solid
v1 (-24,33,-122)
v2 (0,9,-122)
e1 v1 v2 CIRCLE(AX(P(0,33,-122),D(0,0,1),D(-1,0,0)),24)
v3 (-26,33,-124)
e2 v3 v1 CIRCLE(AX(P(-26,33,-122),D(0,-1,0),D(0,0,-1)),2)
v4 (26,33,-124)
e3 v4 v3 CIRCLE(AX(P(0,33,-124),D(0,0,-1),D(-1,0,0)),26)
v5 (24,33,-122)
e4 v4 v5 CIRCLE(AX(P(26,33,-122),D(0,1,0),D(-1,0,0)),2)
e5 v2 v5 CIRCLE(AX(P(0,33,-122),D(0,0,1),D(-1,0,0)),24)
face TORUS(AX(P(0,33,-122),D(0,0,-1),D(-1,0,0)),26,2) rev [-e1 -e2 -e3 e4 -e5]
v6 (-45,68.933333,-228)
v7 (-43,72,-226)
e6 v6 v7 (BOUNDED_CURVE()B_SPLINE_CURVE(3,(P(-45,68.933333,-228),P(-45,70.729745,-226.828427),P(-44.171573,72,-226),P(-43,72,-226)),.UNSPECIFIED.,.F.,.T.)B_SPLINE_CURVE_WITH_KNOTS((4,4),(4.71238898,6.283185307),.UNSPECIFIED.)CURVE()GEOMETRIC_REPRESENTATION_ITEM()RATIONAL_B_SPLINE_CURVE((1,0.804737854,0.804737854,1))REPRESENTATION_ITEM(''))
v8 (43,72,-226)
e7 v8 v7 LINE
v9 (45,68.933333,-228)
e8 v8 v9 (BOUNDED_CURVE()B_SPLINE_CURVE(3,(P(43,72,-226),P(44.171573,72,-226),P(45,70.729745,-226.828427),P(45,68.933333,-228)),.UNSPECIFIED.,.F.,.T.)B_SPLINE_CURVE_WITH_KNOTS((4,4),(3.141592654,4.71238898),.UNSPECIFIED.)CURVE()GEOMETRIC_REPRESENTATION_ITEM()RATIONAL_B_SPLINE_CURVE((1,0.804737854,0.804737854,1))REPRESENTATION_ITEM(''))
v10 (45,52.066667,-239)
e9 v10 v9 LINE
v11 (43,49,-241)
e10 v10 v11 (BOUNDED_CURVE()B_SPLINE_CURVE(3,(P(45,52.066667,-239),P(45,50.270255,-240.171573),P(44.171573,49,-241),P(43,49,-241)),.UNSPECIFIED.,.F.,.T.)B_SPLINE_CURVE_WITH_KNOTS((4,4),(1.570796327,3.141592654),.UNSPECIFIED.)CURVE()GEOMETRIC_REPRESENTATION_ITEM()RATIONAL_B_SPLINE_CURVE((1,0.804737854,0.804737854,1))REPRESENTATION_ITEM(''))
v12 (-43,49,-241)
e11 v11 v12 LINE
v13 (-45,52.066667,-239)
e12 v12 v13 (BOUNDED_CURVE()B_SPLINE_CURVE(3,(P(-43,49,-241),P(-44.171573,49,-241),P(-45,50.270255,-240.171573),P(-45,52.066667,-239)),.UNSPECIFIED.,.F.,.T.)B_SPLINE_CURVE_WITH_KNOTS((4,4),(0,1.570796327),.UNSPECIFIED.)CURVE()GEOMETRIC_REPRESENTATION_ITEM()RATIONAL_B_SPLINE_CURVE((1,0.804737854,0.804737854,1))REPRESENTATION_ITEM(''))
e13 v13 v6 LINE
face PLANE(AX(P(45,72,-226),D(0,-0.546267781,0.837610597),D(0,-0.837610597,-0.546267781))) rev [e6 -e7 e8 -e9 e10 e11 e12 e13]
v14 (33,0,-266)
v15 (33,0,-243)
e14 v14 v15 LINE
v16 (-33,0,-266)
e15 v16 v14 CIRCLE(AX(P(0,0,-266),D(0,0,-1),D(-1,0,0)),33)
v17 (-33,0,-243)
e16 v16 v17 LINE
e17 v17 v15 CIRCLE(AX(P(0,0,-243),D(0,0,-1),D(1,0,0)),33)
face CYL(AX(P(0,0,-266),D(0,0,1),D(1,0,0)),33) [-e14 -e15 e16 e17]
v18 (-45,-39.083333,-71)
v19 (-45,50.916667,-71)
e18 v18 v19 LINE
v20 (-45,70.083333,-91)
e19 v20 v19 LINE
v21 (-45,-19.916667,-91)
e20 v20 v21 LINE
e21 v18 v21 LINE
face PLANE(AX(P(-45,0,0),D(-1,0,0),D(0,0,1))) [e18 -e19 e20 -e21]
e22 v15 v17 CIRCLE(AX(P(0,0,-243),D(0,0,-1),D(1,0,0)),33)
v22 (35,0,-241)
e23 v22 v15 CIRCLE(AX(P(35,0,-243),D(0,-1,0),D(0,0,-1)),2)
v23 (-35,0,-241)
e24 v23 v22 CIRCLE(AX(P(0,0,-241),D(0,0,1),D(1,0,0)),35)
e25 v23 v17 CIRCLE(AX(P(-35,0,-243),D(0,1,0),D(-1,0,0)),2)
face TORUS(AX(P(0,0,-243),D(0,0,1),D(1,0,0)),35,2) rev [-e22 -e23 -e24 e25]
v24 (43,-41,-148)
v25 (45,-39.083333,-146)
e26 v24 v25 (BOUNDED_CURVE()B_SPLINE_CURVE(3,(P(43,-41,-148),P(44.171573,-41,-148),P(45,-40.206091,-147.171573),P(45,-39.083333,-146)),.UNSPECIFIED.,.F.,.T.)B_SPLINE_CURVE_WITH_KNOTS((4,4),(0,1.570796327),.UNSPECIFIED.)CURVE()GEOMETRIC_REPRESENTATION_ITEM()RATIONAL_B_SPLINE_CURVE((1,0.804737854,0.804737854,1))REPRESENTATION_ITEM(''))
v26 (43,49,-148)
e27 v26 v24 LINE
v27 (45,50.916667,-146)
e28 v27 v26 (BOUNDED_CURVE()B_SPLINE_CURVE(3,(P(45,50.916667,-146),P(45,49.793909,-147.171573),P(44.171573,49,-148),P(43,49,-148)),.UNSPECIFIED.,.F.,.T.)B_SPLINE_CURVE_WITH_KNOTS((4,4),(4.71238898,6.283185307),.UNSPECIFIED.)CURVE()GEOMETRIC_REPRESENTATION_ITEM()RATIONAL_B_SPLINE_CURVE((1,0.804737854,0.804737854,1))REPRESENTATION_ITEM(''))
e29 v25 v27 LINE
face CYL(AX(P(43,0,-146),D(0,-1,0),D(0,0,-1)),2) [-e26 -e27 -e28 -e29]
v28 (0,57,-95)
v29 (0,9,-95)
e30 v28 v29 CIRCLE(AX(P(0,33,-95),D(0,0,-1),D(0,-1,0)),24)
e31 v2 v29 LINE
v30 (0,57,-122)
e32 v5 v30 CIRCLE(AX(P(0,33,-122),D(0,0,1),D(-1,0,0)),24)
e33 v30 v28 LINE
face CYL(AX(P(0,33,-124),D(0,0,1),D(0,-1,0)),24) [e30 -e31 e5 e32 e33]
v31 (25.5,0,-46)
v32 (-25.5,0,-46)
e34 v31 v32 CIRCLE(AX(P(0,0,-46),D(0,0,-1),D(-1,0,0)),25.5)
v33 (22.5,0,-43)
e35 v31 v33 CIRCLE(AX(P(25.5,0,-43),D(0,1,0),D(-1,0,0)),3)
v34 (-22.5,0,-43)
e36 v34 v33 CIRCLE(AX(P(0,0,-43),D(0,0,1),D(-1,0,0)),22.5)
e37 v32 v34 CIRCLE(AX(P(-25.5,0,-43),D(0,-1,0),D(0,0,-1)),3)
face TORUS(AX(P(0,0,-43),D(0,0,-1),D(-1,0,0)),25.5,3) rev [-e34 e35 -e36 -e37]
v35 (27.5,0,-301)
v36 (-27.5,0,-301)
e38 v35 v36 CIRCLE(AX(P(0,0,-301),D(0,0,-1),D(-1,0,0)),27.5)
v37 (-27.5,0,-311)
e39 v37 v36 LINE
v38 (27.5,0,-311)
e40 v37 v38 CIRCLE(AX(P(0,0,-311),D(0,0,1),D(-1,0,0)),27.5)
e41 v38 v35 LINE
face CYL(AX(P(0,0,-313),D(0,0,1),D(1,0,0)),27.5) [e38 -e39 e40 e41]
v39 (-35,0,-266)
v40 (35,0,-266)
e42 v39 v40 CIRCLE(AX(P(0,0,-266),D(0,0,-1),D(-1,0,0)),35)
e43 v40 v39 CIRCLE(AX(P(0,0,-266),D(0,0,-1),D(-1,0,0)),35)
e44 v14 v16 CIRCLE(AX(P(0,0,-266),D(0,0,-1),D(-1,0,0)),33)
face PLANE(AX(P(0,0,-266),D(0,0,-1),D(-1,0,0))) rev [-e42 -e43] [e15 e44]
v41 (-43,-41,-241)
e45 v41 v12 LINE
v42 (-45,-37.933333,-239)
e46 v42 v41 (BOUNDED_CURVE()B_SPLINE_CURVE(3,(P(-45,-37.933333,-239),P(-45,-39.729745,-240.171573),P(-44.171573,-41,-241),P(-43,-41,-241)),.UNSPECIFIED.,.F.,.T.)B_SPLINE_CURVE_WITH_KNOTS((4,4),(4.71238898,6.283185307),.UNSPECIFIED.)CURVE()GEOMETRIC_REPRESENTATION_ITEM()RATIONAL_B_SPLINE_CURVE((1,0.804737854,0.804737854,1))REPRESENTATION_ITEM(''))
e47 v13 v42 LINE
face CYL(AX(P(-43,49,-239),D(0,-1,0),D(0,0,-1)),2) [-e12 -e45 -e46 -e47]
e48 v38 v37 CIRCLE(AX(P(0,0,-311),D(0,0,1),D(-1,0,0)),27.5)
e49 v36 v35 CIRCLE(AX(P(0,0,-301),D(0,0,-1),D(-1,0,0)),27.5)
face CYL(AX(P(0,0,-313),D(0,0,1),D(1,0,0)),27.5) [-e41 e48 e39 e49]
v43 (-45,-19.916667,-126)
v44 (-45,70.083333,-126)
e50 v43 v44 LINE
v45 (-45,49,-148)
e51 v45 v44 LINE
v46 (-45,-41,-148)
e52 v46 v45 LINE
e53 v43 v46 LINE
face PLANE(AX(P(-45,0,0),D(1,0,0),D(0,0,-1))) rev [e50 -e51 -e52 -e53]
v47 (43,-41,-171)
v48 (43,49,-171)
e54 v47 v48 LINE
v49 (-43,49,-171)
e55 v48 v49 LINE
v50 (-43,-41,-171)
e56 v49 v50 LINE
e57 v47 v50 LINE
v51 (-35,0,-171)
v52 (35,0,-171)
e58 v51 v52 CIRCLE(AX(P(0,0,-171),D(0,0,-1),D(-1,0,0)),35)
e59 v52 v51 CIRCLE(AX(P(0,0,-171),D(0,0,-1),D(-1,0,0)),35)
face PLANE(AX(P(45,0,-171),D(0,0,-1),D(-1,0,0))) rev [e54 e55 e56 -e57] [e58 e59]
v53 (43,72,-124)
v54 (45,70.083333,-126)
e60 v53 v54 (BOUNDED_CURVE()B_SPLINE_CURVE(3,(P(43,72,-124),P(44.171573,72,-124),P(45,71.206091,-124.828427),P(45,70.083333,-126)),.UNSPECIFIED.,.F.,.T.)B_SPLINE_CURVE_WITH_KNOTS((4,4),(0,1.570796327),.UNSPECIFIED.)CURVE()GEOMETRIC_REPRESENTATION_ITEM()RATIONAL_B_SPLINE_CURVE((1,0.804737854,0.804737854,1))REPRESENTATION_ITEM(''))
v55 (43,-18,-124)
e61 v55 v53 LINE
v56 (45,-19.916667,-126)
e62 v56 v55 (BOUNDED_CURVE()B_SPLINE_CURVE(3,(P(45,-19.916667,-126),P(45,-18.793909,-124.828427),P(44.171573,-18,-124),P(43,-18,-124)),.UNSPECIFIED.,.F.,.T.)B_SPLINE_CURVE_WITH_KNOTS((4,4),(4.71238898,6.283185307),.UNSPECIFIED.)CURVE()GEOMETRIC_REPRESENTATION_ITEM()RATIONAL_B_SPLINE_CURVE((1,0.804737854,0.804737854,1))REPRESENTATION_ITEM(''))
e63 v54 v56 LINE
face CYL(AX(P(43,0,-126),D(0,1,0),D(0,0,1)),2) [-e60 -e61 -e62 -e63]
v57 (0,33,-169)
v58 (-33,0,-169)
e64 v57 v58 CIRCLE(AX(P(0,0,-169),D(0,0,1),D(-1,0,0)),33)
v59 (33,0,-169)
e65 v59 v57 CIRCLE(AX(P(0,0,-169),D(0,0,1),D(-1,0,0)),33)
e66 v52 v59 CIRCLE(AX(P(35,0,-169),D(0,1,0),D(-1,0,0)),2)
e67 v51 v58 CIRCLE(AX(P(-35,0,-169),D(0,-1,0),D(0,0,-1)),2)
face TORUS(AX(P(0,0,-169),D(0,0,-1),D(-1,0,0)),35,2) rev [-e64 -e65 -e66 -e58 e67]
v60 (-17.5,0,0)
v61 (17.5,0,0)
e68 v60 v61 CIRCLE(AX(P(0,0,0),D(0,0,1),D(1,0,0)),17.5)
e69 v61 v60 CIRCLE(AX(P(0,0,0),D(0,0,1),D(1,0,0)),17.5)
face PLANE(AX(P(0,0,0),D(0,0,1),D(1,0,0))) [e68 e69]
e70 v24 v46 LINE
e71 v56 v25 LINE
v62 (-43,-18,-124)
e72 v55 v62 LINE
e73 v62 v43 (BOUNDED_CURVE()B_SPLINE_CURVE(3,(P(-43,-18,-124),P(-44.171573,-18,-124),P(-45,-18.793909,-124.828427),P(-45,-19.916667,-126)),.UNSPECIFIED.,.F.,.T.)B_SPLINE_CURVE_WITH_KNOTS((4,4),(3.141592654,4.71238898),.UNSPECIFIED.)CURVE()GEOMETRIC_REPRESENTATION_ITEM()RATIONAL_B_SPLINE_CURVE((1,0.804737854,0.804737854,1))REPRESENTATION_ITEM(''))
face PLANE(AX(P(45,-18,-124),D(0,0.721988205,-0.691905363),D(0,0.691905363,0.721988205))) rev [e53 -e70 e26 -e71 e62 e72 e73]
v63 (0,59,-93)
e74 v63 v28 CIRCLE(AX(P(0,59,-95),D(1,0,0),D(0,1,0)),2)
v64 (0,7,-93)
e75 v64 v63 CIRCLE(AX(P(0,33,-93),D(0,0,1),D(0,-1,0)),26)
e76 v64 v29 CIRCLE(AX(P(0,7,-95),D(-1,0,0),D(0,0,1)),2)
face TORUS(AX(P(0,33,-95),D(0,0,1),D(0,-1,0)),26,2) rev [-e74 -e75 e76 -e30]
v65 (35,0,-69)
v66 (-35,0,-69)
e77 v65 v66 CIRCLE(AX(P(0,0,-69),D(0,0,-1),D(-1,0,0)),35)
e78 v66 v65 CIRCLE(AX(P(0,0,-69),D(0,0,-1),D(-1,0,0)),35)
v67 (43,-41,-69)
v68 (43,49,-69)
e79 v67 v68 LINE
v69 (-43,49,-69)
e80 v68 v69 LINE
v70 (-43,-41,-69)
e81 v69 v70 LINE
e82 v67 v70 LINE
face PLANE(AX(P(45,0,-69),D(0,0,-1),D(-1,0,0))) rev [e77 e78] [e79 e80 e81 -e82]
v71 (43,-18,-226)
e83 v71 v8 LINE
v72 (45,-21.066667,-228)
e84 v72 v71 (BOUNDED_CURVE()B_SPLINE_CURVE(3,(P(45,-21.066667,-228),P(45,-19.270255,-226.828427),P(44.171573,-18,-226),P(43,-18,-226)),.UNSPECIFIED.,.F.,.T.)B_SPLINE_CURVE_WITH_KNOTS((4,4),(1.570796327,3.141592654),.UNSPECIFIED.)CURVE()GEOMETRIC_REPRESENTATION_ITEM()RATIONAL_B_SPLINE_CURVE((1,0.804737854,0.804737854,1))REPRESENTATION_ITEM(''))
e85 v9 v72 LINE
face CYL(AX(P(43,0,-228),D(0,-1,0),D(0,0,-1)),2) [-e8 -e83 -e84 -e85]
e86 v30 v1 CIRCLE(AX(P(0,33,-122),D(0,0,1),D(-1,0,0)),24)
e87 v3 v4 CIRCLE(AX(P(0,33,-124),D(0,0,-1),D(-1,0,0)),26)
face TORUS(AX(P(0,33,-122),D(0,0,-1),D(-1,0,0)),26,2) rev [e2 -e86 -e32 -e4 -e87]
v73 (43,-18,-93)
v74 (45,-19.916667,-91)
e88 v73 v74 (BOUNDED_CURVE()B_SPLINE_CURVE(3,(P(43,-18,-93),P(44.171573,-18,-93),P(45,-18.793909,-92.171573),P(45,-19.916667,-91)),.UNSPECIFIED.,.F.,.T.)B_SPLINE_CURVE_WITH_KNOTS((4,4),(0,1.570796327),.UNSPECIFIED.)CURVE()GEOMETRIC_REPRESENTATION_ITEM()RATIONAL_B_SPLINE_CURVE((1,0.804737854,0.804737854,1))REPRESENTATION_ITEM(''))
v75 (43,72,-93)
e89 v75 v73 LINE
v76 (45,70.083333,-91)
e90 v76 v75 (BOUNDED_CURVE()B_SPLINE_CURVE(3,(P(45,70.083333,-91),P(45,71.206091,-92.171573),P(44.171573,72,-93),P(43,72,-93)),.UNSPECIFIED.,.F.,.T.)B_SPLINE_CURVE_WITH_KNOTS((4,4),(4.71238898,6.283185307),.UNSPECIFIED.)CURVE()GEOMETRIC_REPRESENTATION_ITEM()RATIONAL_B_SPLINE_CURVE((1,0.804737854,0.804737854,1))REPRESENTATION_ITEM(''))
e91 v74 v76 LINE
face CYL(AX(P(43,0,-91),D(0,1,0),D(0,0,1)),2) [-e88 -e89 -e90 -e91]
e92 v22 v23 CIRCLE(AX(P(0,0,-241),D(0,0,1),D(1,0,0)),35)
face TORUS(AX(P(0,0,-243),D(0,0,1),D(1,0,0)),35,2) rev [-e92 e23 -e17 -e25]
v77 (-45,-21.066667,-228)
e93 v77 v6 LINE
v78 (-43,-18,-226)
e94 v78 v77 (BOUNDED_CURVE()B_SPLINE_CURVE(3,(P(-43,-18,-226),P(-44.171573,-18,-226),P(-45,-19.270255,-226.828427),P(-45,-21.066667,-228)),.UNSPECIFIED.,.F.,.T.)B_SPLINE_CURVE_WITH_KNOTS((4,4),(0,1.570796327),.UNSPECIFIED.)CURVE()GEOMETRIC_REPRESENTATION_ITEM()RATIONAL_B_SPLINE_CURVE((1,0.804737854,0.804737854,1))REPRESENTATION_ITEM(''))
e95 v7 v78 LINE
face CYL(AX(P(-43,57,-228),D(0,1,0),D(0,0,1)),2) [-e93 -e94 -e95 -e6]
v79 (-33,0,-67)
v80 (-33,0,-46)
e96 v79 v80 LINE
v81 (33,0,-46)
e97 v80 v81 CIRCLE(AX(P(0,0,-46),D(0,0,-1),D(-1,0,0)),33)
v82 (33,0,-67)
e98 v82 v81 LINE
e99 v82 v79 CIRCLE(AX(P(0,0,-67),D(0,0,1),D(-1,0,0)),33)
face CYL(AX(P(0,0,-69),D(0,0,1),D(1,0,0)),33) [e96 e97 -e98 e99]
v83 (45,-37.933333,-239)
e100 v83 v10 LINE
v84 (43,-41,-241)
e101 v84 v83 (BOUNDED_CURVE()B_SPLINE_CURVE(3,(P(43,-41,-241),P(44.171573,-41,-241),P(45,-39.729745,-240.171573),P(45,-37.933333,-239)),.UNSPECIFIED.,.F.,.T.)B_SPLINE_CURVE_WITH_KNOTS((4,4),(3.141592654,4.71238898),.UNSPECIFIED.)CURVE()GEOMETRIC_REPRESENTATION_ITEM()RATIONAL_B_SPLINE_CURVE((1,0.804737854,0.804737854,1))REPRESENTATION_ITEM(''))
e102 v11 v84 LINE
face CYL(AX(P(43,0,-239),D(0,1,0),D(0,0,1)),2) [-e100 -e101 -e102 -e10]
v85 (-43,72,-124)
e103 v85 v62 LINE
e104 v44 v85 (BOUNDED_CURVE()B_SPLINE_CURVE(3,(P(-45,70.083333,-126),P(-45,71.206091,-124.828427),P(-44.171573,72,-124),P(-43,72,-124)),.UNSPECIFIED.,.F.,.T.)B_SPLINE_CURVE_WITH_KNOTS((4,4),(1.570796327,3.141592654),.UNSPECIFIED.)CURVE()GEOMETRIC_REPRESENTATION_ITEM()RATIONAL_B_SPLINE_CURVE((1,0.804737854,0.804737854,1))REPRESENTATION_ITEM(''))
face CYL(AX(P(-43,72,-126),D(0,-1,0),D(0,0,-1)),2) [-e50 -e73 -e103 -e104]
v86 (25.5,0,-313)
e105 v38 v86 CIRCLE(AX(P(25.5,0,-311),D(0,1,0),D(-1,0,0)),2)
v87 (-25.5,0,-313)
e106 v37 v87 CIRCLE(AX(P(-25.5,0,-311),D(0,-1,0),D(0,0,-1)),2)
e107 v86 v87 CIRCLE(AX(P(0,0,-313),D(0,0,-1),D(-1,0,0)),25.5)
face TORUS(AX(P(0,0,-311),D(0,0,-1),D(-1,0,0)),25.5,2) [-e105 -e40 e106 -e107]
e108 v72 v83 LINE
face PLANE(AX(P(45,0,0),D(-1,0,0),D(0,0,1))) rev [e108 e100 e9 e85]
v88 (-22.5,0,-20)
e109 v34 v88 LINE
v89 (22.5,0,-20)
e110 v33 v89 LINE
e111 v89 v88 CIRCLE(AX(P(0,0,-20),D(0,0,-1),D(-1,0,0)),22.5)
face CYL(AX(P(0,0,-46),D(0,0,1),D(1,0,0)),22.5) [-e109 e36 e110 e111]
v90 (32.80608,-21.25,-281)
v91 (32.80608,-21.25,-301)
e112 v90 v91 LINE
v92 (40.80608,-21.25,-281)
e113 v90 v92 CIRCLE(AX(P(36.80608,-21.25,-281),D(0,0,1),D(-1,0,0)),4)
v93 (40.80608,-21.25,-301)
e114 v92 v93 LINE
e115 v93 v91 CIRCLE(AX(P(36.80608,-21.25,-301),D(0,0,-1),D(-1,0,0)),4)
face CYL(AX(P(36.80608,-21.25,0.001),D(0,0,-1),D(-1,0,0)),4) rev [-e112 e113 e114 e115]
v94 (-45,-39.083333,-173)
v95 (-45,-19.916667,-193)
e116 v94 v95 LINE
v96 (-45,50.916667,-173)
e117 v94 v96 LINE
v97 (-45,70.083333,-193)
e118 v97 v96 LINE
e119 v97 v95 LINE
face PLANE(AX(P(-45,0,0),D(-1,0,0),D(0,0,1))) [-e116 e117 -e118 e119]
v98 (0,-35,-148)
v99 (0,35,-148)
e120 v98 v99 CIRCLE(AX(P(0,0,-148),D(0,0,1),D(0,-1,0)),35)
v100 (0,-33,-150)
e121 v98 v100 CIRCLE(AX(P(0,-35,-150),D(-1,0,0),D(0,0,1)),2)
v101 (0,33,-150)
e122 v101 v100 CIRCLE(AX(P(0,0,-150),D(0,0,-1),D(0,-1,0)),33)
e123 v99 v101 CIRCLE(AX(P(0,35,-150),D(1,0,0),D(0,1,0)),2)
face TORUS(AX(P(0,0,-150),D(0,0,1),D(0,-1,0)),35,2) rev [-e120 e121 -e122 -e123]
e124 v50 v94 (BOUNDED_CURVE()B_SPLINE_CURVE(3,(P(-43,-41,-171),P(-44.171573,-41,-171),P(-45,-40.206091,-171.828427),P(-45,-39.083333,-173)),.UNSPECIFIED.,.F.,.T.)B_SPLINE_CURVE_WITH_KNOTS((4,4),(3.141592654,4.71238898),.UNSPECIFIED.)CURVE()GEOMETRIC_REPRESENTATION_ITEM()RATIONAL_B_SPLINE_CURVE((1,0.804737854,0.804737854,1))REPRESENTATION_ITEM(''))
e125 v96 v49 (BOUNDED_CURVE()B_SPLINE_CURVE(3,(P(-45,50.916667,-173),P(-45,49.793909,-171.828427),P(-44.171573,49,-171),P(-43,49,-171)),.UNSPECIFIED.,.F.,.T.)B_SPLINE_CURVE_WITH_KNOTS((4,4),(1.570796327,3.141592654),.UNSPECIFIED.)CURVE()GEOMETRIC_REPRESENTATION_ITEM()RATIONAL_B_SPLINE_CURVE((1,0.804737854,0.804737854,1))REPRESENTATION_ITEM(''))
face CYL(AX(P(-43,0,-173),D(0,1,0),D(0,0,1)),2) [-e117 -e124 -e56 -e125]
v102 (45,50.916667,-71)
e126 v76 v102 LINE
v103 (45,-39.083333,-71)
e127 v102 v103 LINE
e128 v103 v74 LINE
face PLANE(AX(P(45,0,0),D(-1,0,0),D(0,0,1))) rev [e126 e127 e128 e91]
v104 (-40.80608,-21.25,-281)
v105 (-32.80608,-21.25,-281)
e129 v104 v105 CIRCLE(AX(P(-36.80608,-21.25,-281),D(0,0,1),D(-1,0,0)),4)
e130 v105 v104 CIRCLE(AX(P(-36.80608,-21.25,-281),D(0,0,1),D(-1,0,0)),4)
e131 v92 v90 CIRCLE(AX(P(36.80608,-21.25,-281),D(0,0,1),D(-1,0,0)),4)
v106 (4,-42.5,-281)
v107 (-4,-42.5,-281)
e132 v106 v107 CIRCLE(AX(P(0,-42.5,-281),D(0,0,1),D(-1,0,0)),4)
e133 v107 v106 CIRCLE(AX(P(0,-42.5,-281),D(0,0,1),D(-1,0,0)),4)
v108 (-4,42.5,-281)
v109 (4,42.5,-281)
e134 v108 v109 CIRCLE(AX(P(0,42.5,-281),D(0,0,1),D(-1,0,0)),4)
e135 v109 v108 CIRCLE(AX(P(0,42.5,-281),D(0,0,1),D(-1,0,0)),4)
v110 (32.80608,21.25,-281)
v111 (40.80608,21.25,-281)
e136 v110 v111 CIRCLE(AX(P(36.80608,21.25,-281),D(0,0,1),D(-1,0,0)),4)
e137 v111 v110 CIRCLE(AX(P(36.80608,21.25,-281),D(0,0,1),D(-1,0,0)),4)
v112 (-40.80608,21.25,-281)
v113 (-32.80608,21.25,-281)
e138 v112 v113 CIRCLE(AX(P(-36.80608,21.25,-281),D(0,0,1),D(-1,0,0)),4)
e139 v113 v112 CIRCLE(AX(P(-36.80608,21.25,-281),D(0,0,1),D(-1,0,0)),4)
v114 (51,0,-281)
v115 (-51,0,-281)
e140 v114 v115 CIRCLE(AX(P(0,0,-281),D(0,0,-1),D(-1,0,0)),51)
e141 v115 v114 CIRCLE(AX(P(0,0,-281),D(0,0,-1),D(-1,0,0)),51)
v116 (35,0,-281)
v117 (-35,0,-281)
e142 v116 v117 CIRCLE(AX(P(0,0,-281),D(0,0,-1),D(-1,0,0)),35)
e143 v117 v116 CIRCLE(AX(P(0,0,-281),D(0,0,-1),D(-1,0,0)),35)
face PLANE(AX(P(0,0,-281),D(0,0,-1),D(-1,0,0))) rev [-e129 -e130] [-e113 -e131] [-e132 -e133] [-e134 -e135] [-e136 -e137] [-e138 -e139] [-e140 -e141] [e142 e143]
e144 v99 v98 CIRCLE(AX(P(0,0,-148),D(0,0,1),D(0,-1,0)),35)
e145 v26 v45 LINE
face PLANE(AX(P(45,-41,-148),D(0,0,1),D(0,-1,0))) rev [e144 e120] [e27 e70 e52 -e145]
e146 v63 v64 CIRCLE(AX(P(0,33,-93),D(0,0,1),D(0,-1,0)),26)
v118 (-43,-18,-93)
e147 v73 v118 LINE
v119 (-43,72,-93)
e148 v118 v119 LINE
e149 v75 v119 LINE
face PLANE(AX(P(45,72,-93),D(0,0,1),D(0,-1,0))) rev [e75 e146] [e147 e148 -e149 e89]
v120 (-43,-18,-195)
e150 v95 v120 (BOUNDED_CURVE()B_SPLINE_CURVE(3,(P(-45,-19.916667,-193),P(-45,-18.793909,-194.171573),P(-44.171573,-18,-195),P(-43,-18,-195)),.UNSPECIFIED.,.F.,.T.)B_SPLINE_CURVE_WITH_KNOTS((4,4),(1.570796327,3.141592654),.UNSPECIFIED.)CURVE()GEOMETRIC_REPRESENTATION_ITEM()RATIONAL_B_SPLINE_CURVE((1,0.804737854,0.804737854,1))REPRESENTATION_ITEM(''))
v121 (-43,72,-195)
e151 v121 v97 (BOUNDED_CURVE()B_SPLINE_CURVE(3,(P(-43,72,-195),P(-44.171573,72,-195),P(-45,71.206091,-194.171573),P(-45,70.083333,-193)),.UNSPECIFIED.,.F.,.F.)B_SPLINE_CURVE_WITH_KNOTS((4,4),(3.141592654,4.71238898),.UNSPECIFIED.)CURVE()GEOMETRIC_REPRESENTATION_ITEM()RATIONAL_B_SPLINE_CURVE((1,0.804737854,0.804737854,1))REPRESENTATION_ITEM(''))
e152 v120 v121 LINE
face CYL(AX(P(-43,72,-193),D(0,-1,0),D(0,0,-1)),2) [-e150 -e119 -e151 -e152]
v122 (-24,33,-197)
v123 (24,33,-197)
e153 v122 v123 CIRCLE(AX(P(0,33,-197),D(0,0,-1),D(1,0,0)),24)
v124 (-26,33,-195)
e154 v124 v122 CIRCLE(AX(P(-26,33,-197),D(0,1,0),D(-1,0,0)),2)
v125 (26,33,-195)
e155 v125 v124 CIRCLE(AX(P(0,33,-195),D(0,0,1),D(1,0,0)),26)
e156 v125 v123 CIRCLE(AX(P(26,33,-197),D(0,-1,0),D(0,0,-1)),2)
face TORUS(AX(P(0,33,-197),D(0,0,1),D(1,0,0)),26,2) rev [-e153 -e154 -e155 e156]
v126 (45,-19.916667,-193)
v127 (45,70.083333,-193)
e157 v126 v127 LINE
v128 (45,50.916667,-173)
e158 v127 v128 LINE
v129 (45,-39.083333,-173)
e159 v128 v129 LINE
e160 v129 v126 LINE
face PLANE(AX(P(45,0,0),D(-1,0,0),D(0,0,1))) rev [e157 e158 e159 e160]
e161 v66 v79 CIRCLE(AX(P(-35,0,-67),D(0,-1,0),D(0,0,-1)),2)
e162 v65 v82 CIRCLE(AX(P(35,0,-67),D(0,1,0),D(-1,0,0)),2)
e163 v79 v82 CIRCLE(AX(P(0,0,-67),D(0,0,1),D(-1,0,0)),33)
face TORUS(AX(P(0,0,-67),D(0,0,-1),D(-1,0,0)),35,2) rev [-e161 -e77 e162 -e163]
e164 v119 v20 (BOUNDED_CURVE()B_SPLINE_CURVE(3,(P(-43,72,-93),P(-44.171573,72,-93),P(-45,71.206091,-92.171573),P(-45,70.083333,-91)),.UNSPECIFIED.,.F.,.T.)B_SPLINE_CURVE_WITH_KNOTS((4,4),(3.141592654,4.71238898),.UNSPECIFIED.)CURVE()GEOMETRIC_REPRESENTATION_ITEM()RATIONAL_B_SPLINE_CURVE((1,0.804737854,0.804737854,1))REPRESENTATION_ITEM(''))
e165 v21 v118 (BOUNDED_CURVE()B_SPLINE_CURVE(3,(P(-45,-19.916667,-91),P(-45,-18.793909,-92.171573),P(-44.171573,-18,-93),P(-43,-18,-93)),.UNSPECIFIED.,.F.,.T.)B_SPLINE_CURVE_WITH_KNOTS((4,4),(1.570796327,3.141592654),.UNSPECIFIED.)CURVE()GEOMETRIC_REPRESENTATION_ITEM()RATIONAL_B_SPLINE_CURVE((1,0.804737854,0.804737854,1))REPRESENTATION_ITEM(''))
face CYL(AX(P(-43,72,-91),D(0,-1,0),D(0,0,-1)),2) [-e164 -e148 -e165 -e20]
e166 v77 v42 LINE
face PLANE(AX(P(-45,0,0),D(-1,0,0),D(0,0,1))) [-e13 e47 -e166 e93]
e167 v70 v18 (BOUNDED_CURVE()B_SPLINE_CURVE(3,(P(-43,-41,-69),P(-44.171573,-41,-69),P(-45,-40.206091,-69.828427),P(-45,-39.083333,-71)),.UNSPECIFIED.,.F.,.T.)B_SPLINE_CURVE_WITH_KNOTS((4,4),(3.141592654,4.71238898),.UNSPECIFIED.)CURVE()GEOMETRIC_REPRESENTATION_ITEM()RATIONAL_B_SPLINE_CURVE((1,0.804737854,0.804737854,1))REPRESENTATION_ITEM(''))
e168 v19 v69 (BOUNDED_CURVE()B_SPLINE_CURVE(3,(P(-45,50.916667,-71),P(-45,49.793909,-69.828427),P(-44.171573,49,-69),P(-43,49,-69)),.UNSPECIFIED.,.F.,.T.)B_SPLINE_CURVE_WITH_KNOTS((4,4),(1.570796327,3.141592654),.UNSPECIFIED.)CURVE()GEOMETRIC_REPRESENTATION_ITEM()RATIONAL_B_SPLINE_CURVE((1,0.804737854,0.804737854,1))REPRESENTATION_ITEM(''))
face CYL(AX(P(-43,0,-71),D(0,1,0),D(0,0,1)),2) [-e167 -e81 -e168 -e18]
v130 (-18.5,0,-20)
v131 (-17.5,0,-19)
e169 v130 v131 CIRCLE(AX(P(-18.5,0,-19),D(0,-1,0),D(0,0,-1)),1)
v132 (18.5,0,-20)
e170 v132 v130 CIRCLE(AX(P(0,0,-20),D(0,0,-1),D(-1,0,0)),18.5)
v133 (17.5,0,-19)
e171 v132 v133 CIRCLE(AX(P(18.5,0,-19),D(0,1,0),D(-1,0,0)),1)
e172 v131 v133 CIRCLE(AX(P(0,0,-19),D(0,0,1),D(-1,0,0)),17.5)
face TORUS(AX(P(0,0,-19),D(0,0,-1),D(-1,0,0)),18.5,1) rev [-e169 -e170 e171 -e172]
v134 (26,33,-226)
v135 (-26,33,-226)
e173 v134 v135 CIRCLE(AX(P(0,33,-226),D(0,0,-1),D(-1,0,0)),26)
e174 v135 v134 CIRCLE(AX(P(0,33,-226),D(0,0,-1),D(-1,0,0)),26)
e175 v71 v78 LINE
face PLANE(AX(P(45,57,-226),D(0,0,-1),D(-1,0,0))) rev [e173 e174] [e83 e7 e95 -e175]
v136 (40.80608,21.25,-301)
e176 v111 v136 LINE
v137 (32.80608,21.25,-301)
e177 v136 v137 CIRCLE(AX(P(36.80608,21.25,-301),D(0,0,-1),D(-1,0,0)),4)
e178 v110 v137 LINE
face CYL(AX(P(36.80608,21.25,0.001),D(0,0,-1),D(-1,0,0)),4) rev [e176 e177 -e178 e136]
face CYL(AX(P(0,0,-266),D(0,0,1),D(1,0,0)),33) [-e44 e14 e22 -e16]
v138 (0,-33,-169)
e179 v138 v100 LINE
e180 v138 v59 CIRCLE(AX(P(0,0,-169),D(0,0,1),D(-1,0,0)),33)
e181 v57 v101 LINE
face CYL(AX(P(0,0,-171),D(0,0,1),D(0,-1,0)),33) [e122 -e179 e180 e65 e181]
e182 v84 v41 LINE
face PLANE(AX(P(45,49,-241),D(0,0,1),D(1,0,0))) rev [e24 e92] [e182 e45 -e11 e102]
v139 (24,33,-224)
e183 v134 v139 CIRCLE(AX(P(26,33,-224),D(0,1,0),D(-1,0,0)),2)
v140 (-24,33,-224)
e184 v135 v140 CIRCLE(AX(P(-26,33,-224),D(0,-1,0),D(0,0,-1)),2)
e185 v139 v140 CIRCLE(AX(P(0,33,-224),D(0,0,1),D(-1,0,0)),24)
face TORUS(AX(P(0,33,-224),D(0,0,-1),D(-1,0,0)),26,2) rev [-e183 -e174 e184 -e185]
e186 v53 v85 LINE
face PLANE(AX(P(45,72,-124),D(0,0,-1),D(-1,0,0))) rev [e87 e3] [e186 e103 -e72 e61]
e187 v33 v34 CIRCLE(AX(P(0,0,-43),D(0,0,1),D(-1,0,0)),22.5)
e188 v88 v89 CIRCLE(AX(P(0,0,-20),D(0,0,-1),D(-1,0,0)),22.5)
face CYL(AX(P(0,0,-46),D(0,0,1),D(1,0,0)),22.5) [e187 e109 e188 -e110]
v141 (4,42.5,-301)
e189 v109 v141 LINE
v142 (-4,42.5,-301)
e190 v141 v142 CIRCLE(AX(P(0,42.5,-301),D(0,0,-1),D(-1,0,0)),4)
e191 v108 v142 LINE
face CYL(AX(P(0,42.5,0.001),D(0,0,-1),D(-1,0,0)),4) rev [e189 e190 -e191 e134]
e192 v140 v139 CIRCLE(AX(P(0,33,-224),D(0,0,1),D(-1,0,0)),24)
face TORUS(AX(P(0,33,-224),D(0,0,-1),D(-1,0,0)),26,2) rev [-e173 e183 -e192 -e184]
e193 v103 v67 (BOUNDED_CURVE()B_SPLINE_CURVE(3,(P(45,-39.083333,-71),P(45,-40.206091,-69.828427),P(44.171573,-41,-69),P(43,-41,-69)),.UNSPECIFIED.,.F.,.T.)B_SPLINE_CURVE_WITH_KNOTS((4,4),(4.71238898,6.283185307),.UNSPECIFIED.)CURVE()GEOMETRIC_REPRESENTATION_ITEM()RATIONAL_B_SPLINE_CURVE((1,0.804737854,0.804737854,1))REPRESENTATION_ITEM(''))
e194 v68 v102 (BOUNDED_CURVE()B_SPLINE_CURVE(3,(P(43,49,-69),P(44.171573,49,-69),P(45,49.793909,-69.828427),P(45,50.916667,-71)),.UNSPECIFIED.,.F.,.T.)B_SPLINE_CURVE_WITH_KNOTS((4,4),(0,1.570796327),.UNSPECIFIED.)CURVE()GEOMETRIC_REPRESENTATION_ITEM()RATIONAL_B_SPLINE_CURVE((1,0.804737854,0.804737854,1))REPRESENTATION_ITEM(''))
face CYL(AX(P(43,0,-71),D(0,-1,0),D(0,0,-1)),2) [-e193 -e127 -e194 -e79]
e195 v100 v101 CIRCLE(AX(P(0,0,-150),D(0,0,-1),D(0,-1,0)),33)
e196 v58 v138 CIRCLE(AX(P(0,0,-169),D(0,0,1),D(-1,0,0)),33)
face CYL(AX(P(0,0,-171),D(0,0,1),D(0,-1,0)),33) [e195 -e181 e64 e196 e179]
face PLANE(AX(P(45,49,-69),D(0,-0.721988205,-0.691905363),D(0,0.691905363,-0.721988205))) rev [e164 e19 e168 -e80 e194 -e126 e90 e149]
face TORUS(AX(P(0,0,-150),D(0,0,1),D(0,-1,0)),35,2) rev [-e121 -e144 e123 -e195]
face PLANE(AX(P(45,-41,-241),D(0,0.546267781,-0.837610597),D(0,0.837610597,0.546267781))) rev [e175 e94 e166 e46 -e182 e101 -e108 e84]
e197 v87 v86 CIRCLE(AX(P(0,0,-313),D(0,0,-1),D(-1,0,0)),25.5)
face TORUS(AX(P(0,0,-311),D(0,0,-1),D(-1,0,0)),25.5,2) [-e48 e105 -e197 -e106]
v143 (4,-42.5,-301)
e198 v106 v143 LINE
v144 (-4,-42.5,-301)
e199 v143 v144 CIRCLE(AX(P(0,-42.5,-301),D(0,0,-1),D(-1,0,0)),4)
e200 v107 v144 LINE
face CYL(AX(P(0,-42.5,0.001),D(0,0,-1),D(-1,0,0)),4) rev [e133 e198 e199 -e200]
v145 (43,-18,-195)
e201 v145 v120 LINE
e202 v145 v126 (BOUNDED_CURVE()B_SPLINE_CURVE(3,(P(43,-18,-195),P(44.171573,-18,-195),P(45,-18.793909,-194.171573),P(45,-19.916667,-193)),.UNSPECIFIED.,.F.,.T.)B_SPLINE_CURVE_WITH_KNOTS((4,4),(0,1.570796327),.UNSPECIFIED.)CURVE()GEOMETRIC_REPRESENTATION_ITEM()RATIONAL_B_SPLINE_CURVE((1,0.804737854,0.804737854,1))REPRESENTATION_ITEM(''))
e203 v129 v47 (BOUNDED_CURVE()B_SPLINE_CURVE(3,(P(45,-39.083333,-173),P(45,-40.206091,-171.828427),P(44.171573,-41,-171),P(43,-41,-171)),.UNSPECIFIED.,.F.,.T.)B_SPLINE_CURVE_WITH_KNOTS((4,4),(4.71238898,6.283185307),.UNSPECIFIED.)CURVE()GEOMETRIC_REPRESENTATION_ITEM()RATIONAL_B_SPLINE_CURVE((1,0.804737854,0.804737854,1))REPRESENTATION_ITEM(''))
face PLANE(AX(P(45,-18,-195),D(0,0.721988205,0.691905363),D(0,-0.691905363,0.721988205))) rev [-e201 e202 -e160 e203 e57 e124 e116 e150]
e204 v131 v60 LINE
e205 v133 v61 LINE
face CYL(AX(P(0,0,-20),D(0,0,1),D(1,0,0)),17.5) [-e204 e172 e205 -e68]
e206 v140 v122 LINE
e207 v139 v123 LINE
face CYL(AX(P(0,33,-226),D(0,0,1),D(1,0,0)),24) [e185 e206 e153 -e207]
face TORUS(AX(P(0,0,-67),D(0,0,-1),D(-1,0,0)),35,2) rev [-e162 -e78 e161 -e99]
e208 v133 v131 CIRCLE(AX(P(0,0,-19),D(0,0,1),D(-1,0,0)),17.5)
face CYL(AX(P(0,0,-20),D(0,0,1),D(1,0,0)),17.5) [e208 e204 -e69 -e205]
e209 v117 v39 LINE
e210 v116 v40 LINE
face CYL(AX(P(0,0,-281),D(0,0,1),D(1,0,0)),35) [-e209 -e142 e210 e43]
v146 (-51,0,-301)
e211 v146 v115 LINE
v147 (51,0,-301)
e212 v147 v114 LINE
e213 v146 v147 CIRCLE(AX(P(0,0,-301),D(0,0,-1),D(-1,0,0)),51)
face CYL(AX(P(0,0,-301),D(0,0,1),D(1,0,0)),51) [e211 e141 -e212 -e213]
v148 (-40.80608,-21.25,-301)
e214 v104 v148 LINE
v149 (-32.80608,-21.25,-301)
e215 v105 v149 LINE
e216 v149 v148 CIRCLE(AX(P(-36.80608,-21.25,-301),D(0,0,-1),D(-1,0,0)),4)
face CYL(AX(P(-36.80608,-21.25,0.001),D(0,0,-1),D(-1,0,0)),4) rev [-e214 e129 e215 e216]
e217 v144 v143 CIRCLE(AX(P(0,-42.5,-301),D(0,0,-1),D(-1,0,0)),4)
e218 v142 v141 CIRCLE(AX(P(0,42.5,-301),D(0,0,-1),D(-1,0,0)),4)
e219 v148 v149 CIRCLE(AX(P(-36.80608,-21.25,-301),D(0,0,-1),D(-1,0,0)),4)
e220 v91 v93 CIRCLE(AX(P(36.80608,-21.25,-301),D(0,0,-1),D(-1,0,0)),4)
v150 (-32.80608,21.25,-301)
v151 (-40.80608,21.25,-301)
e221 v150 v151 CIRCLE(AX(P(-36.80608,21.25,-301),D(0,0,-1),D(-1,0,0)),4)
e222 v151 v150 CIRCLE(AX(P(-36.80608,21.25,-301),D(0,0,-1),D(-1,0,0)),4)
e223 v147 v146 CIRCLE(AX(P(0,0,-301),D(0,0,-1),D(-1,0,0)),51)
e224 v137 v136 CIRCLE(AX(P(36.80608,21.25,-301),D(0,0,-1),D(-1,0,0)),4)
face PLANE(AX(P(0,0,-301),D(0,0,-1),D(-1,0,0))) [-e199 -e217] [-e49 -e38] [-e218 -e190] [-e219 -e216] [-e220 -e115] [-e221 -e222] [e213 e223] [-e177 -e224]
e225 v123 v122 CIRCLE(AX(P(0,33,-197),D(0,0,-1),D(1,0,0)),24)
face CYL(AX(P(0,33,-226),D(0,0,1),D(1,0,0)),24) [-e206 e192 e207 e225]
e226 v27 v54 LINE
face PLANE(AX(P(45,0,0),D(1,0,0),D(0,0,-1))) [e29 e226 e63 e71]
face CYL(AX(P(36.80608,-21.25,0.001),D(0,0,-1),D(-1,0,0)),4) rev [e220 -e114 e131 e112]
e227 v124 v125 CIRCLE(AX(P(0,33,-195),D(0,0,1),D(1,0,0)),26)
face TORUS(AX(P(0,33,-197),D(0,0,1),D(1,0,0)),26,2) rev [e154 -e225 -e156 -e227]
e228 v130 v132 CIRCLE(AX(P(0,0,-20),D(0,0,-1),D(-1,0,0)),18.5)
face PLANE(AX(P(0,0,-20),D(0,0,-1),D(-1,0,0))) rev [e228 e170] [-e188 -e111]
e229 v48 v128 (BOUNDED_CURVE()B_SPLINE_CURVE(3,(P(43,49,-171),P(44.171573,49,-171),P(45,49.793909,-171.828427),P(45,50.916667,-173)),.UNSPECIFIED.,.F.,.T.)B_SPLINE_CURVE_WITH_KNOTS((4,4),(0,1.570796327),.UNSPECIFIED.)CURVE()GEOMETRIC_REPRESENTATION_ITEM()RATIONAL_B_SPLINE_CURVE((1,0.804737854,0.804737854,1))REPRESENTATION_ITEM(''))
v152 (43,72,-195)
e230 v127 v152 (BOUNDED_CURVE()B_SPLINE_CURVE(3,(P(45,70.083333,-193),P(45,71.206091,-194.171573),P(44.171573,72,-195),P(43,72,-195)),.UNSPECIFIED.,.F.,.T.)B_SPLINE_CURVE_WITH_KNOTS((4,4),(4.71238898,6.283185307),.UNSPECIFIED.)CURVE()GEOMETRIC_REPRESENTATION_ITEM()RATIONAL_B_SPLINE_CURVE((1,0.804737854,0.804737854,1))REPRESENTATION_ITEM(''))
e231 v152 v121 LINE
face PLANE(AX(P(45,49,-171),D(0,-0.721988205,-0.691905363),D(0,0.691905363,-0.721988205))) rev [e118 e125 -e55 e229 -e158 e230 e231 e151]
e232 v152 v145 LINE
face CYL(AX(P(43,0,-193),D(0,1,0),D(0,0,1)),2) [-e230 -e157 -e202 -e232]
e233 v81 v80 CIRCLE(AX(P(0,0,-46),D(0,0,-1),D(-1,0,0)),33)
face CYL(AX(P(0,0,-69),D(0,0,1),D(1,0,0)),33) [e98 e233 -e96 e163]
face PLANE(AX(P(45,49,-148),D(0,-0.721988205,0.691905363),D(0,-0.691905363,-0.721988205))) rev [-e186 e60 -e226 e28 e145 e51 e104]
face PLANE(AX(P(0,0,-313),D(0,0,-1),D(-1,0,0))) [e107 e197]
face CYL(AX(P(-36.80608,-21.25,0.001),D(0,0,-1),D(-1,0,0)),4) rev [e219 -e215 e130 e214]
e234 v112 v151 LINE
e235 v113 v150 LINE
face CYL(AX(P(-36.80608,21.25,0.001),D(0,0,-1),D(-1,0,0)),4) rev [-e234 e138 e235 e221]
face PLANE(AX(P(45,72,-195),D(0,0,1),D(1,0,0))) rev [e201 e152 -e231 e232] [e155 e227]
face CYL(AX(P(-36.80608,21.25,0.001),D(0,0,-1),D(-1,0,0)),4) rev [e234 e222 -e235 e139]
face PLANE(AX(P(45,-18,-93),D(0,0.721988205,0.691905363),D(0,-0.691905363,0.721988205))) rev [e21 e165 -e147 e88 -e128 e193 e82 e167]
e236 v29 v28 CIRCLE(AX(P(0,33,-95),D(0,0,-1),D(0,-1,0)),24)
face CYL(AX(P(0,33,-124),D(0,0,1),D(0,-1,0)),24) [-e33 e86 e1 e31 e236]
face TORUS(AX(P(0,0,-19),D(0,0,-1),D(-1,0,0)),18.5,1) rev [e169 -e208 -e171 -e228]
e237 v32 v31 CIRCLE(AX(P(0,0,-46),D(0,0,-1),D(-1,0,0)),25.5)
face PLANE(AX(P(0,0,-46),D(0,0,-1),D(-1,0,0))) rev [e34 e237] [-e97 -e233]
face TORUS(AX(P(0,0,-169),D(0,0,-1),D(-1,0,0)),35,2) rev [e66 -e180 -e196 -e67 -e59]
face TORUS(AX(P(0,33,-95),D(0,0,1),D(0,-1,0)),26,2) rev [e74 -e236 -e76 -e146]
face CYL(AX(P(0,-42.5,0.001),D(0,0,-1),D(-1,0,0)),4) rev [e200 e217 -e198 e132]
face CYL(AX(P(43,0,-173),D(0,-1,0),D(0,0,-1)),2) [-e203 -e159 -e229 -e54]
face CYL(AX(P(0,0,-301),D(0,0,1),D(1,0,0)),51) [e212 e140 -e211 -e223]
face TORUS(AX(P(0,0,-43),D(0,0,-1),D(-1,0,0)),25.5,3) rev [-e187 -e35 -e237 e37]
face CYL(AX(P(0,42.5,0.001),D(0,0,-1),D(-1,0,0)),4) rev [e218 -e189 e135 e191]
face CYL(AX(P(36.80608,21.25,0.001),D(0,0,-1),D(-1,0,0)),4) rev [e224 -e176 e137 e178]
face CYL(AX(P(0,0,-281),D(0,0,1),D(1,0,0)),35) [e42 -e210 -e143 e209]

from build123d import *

# Parameters (mm, degrees)
FRONT_JOURNAL_35_SKETCH_R          = 17.5
FRONT_JOURNAL_35_DEPTH             = 20
SHAFT_STEP_45_SKETCH_R             = 22.5
SHAFT_STEP_45_DEPTH                = 26
FRONT_MAIN_JOURNAL_66_SKETCH_R     = 33
FRONT_MAIN_JOURNAL_66_DEPTH        = 23
CRANK_WEB_1_DEPTH                  = 45
CRANKPIN_1_48_SKETCH_R             = 24
CRANKPIN_1_48_DEPTH                = 31
CRANK_WEB_2_DEPTH                  = 45
CENTRE_MAIN_JOURNAL_66_SKETCH_R    = 33
CENTRE_MAIN_JOURNAL_66_DEPTH       = 23
CRANK_WEB_3_DEPTH                  = 45
CRANKPIN_2_SKETCH_R                = 24
CRANKPIN_2_DEPTH                   = 31
CRANK_WEB_4_DEPTH                  = 45
REAR_MAIN_JOURNAL_SKETCH_R         = 33
REAR_MAIN_JOURNAL_DEPTH            = 25
FLANGE_NECK_70_SKETCH_R            = 35
FLANGE_NECK_70_DEPTH               = 15
REAR_FLANGE_102_SKETCH_R           = 51
REAR_FLANGE_102_DEPTH              = 20
FLANGE_SPIGOT_55_SKETCH_R          = 27.5
FLANGE_SPIGOT_55_DEPTH             = 12
FLANGE_BOLT_HOLES_6X_8_PCD85_REACH = 315.665
FLANGE_BOLT_HOLES_SKETCH_R         = 4
FRONT_JOURNAL_FILLET_R1_R          = 1
SHAFT_STEP_FILLET_R3_R             = 3
JOURNAL_AND_CRANKPIN_FILLETS_R2_R  = 2
CRANK_WEB_1_EDGE_FILLET_R2_R       = 2
CRANK_WEBS_2_4_EDGE_FILLETS_R2_R   = 2


with BuildPart() as part:
    # Front Journal Ø35 Sketch → Front Journal Ø35 (new body)
    with BuildSketch(Plane.XY):
        Circle(FRONT_JOURNAL_35_SKETCH_R)
    extrude(amount=-FRONT_JOURNAL_35_DEPTH)

    # Shaft Step Ø45 Sketch → Shaft Step Ø45 (add)
    with BuildSketch(Plane(origin=(0, 0, -20), x_dir=(-1, 0, 0), z_dir=(0, 0, -1))):
        with Locations(Location((0, 0, 0), (0, 0, 180))):
            Circle(SHAFT_STEP_45_SKETCH_R)
    extrude(amount=SHAFT_STEP_45_DEPTH)

    # Front Main Journal Ø66 Sketch → Front Main Journal Ø66 (add)
    with BuildSketch(Plane(origin=(0, 0, -46), x_dir=(-1, 0, 0), z_dir=(0, 0, -1))):
        Circle(FRONT_MAIN_JOURNAL_66_SKETCH_R)
    extrude(amount=FRONT_MAIN_JOURNAL_66_DEPTH)

    # Crank Web 1 Profile → Crank Web 1 (add, symmetric)
    with BuildSketch(Plane(origin=(0, 0, 0), x_dir=(0, 0, -1), z_dir=(1, 0, 0))):
        Polygon((69, 0), (69, 49), (93, 72), (93, -18), (69, -41), align=None)
    extrude(amount=CRANK_WEB_1_DEPTH, both=True)

    # Crankpin 1 Ø48 Sketch → Crankpin 1 Ø48 (add)
    with BuildSketch(Plane(origin=(0, 0, -93), x_dir=(-1, 0, 0), z_dir=(0, 0, -1))):
        with Locations(Location((0, 33, 0), (0, 0, 90))):
            Circle(CRANKPIN_1_48_SKETCH_R)
    extrude(amount=CRANKPIN_1_48_DEPTH)

    # Crank Web 2 Profile → Crank Web 2 (add, symmetric)
    with BuildSketch(Plane(origin=(0, 0, 0), x_dir=(0, 0, -1), z_dir=(1, 0, 0))):
        Polygon((124, 72), (124, -18), (148, -41), (148, 49), align=None)
    extrude(amount=CRANK_WEB_2_DEPTH, both=True)

    # Centre Main Journal Ø66 Sketch → Centre Main Journal Ø66 (add)
    with BuildSketch(Plane(origin=(0, 0, -148), x_dir=(-1, 0, 0), z_dir=(0, 0, -1))):
        Circle(CENTRE_MAIN_JOURNAL_66_SKETCH_R)
    extrude(amount=CENTRE_MAIN_JOURNAL_66_DEPTH)

    # Crank Web 3 Profile → Crank Web 3 (add, symmetric)
    with BuildSketch(Plane(origin=(0, 0, 0), x_dir=(0, 0, -1), z_dir=(1, 0, 0))):
        Polygon((171, 0), (171, 49), (195, 72), (195, -18), (171, -41), align=None)
    extrude(amount=CRANK_WEB_3_DEPTH, both=True)

    # Crankpin 2 Sketch → Crankpin 2 (add)
    with BuildSketch(Plane(origin=(0, 0, -195), x_dir=(-1, 0, 0), z_dir=(0, 0, -1))):
        with Locations(Location((0, 33, 0), (0, 0, 90))):
            Circle(CRANKPIN_2_SKETCH_R)
    extrude(amount=CRANKPIN_2_DEPTH)

    # Crank Web 4 Profile → Crank Web 4 (add, symmetric)
    with BuildSketch(Plane(origin=(0, 0, 0), x_dir=(0, 0, -1), z_dir=(1, 0, 0))):
        Polygon((226, 57), (226, 72), (241, 49), (241, -41), (226, -18), align=None)
    extrude(amount=CRANK_WEB_4_DEPTH, both=True)

    # Rear Main Journal Sketch → Rear Main Journal (add)
    with BuildSketch(Plane(origin=(0, 0, -241), x_dir=(-1, 0, 0), z_dir=(0, 0, -1))):
        Circle(REAR_MAIN_JOURNAL_SKETCH_R)
    extrude(amount=REAR_MAIN_JOURNAL_DEPTH)

    # Flange Neck Ø70 Sketch → Flange Neck Ø70 (add)
    with BuildSketch(Plane(origin=(0, 0, -266), x_dir=(-1, 0, 0), z_dir=(0, 0, -1))):
        Circle(FLANGE_NECK_70_SKETCH_R)
    extrude(amount=FLANGE_NECK_70_DEPTH)

    # Rear Flange Ø102 Sketch → Rear Flange Ø102 (add)
    with BuildSketch(Plane(origin=(0, 0, -281), x_dir=(-1, 0, 0), z_dir=(0, 0, -1))):
        Circle(REAR_FLANGE_102_SKETCH_R)
    extrude(amount=REAR_FLANGE_102_DEPTH)

    # Flange Spigot Ø55 Sketch → Flange Spigot Ø55 (add)
    with BuildSketch(Plane(origin=(0, 0, -301), x_dir=(-1, 0, 0), z_dir=(0, 0, -1))):
        Circle(FLANGE_SPIGOT_55_SKETCH_R)
    extrude(amount=FLANGE_SPIGOT_55_DEPTH)

    # Flange Bolt Holes Sketch → Flange Bolt Holes 6xØ8 PCD85 (cut, up to next)
    with BuildSketch(Plane(origin=(0, 0, -301), x_dir=(-1, 0, 0), z_dir=(0, 0, -1)), mode=Mode.PRIVATE) as flange_bolt_holes_6x_8_pcd85_sk1:
        with Locations((0, 42.5)):
            Circle(FLANGE_BOLT_HOLES_SKETCH_R)
    flange_bolt_holes_6x_8_pcd85_tool1 = extrude(flange_bolt_holes_6x_8_pcd85_sk1.sketch, amount=-FLANGE_BOLT_HOLES_6X_8_PCD85_REACH, mode=Mode.PRIVATE) & part.part
    # Flange Bolt Holes Sketch → Flange Bolt Holes 6xØ8 PCD85 (cut, up to next)
    with BuildSketch(Plane(origin=(0, 0, -301), x_dir=(-1, 0, 0), z_dir=(0, 0, -1)), mode=Mode.PRIVATE) as flange_bolt_holes_6x_8_pcd85_sk2:
        with Locations((36.806079661, 21.25)):
            Circle(FLANGE_BOLT_HOLES_SKETCH_R)
    flange_bolt_holes_6x_8_pcd85_tool2 = extrude(flange_bolt_holes_6x_8_pcd85_sk2.sketch, amount=-FLANGE_BOLT_HOLES_6X_8_PCD85_REACH, mode=Mode.PRIVATE) & part.part
    # Flange Bolt Holes Sketch → Flange Bolt Holes 6xØ8 PCD85 (cut, up to next)
    with BuildSketch(Plane(origin=(0, 0, -301), x_dir=(-1, 0, 0), z_dir=(0, 0, -1)), mode=Mode.PRIVATE) as flange_bolt_holes_6x_8_pcd85_sk3:
        with Locations((36.806079661, -21.25)):
            Circle(FLANGE_BOLT_HOLES_SKETCH_R)
    flange_bolt_holes_6x_8_pcd85_tool3 = extrude(flange_bolt_holes_6x_8_pcd85_sk3.sketch, amount=-FLANGE_BOLT_HOLES_6X_8_PCD85_REACH, mode=Mode.PRIVATE) & part.part
    # Flange Bolt Holes Sketch → Flange Bolt Holes 6xØ8 PCD85 (cut, up to next)
    with BuildSketch(Plane(origin=(0, 0, -301), x_dir=(-1, 0, 0), z_dir=(0, 0, -1)), mode=Mode.PRIVATE) as flange_bolt_holes_6x_8_pcd85_sk4:
        with Locations((0, -42.5)):
            Circle(FLANGE_BOLT_HOLES_SKETCH_R)
    flange_bolt_holes_6x_8_pcd85_tool4 = extrude(flange_bolt_holes_6x_8_pcd85_sk4.sketch, amount=-FLANGE_BOLT_HOLES_6X_8_PCD85_REACH, mode=Mode.PRIVATE) & part.part
    # Flange Bolt Holes Sketch → Flange Bolt Holes 6xØ8 PCD85 (cut, up to next)
    with BuildSketch(Plane(origin=(0, 0, -301), x_dir=(-1, 0, 0), z_dir=(0, 0, -1)), mode=Mode.PRIVATE) as flange_bolt_holes_6x_8_pcd85_sk5:
        with Locations((-36.806079661, -21.25)):
            Circle(FLANGE_BOLT_HOLES_SKETCH_R)
    flange_bolt_holes_6x_8_pcd85_tool5 = extrude(flange_bolt_holes_6x_8_pcd85_sk5.sketch, amount=-FLANGE_BOLT_HOLES_6X_8_PCD85_REACH, mode=Mode.PRIVATE) & part.part
    # Flange Bolt Holes Sketch → Flange Bolt Holes 6xØ8 PCD85 (cut, up to next)
    with BuildSketch(Plane(origin=(0, 0, -301), x_dir=(-1, 0, 0), z_dir=(0, 0, -1)), mode=Mode.PRIVATE) as flange_bolt_holes_6x_8_pcd85_sk6:
        with Locations((-36.806079661, 21.25)):
            Circle(FLANGE_BOLT_HOLES_SKETCH_R)
    flange_bolt_holes_6x_8_pcd85_tool6 = extrude(flange_bolt_holes_6x_8_pcd85_sk6.sketch, amount=-FLANGE_BOLT_HOLES_6X_8_PCD85_REACH, mode=Mode.PRIVATE) & part.part
    add(flange_bolt_holes_6x_8_pcd85_tool1.solids().sort_by_distance((0, 42.5, -301))[0], mode=Mode.SUBTRACT)
    add(flange_bolt_holes_6x_8_pcd85_tool2.solids().sort_by_distance((-36.80608, 21.25, -301))[0], mode=Mode.SUBTRACT)
    add(flange_bolt_holes_6x_8_pcd85_tool3.solids().sort_by_distance((-36.80608, -21.25, -301))[0], mode=Mode.SUBTRACT)
    add(flange_bolt_holes_6x_8_pcd85_tool4.solids().sort_by_distance((0, -42.5, -301))[0], mode=Mode.SUBTRACT)
    add(flange_bolt_holes_6x_8_pcd85_tool5.solids().sort_by_distance((36.80608, -21.25, -301))[0], mode=Mode.SUBTRACT)
    add(flange_bolt_holes_6x_8_pcd85_tool6.solids().sort_by_distance((36.80608, 21.25, -301))[0], mode=Mode.SUBTRACT)

    # Front Journal Fillet R1
    front_journal_fillet_r1_edges = [part.edges().sort_by_distance(p)[0] for p in [
        (-17.5, 0, -20),
    ]]
    fillet(front_journal_fillet_r1_edges, radius=FRONT_JOURNAL_FILLET_R1_R)

    # Shaft Step Fillet R3
    shaft_step_fillet_r3_edges = [part.edges().sort_by_distance(p)[0] for p in [
        (-22.5, 0, -46),
    ]]
    fillet(shaft_step_fillet_r3_edges, radius=SHAFT_STEP_FILLET_R3_R)

    # Journal and Crankpin Fillets R2
    journal_and_crankpin_fillets_r2_edges = [part.edges().sort_by_distance(p)[0] for p in [
        (33, 0, -69),
        (0, 9, -93),
        (0, 9, -124),
        (33, 0, -148),
        (33, 0, -171),
        (0, 9, -195),
        (0, 9, -226),
        (33, 0, -241),
        (27.5, 0, -313),
    ]]
    fillet(journal_and_crankpin_fillets_r2_edges, radius=JOURNAL_AND_CRANKPIN_FILLETS_R2_R)

    # Crank Web 1 Edge Fillet R2
    crank_web_1_edge_fillet_r2_edges = [part.edges().sort_by_distance(p)[0] for p in [
        (-45, 27, -93),
        (-45, 4, -69),
        (45, 4, -69),
        (45, 27, -93),
    ]]
    fillet(crank_web_1_edge_fillet_r2_edges, radius=CRANK_WEB_1_EDGE_FILLET_R2_R)

    # Crank Webs 2-4 Edge Fillets R2
    crank_webs_2_4_edge_fillets_r2_edges = [part.edges().sort_by_distance(p)[0] for p in [
        (-45, 27, -124),
        (45, 27, -124),
        (45, 4, -148),
        (-45, 27, -195),
        (-45, 4, -171),
        (45, 4, -171),
        (45, 27, -195),
        (-45, 4, -241),
        (-45, 27, -226),
        (45, 27, -226),
        (45, 4, -241),
    ]]
    fillet(crank_webs_2_4_edge_fillets_r2_edges, radius=CRANK_WEBS_2_4_EDGE_FILLETS_R2_R)


solid = part.part
